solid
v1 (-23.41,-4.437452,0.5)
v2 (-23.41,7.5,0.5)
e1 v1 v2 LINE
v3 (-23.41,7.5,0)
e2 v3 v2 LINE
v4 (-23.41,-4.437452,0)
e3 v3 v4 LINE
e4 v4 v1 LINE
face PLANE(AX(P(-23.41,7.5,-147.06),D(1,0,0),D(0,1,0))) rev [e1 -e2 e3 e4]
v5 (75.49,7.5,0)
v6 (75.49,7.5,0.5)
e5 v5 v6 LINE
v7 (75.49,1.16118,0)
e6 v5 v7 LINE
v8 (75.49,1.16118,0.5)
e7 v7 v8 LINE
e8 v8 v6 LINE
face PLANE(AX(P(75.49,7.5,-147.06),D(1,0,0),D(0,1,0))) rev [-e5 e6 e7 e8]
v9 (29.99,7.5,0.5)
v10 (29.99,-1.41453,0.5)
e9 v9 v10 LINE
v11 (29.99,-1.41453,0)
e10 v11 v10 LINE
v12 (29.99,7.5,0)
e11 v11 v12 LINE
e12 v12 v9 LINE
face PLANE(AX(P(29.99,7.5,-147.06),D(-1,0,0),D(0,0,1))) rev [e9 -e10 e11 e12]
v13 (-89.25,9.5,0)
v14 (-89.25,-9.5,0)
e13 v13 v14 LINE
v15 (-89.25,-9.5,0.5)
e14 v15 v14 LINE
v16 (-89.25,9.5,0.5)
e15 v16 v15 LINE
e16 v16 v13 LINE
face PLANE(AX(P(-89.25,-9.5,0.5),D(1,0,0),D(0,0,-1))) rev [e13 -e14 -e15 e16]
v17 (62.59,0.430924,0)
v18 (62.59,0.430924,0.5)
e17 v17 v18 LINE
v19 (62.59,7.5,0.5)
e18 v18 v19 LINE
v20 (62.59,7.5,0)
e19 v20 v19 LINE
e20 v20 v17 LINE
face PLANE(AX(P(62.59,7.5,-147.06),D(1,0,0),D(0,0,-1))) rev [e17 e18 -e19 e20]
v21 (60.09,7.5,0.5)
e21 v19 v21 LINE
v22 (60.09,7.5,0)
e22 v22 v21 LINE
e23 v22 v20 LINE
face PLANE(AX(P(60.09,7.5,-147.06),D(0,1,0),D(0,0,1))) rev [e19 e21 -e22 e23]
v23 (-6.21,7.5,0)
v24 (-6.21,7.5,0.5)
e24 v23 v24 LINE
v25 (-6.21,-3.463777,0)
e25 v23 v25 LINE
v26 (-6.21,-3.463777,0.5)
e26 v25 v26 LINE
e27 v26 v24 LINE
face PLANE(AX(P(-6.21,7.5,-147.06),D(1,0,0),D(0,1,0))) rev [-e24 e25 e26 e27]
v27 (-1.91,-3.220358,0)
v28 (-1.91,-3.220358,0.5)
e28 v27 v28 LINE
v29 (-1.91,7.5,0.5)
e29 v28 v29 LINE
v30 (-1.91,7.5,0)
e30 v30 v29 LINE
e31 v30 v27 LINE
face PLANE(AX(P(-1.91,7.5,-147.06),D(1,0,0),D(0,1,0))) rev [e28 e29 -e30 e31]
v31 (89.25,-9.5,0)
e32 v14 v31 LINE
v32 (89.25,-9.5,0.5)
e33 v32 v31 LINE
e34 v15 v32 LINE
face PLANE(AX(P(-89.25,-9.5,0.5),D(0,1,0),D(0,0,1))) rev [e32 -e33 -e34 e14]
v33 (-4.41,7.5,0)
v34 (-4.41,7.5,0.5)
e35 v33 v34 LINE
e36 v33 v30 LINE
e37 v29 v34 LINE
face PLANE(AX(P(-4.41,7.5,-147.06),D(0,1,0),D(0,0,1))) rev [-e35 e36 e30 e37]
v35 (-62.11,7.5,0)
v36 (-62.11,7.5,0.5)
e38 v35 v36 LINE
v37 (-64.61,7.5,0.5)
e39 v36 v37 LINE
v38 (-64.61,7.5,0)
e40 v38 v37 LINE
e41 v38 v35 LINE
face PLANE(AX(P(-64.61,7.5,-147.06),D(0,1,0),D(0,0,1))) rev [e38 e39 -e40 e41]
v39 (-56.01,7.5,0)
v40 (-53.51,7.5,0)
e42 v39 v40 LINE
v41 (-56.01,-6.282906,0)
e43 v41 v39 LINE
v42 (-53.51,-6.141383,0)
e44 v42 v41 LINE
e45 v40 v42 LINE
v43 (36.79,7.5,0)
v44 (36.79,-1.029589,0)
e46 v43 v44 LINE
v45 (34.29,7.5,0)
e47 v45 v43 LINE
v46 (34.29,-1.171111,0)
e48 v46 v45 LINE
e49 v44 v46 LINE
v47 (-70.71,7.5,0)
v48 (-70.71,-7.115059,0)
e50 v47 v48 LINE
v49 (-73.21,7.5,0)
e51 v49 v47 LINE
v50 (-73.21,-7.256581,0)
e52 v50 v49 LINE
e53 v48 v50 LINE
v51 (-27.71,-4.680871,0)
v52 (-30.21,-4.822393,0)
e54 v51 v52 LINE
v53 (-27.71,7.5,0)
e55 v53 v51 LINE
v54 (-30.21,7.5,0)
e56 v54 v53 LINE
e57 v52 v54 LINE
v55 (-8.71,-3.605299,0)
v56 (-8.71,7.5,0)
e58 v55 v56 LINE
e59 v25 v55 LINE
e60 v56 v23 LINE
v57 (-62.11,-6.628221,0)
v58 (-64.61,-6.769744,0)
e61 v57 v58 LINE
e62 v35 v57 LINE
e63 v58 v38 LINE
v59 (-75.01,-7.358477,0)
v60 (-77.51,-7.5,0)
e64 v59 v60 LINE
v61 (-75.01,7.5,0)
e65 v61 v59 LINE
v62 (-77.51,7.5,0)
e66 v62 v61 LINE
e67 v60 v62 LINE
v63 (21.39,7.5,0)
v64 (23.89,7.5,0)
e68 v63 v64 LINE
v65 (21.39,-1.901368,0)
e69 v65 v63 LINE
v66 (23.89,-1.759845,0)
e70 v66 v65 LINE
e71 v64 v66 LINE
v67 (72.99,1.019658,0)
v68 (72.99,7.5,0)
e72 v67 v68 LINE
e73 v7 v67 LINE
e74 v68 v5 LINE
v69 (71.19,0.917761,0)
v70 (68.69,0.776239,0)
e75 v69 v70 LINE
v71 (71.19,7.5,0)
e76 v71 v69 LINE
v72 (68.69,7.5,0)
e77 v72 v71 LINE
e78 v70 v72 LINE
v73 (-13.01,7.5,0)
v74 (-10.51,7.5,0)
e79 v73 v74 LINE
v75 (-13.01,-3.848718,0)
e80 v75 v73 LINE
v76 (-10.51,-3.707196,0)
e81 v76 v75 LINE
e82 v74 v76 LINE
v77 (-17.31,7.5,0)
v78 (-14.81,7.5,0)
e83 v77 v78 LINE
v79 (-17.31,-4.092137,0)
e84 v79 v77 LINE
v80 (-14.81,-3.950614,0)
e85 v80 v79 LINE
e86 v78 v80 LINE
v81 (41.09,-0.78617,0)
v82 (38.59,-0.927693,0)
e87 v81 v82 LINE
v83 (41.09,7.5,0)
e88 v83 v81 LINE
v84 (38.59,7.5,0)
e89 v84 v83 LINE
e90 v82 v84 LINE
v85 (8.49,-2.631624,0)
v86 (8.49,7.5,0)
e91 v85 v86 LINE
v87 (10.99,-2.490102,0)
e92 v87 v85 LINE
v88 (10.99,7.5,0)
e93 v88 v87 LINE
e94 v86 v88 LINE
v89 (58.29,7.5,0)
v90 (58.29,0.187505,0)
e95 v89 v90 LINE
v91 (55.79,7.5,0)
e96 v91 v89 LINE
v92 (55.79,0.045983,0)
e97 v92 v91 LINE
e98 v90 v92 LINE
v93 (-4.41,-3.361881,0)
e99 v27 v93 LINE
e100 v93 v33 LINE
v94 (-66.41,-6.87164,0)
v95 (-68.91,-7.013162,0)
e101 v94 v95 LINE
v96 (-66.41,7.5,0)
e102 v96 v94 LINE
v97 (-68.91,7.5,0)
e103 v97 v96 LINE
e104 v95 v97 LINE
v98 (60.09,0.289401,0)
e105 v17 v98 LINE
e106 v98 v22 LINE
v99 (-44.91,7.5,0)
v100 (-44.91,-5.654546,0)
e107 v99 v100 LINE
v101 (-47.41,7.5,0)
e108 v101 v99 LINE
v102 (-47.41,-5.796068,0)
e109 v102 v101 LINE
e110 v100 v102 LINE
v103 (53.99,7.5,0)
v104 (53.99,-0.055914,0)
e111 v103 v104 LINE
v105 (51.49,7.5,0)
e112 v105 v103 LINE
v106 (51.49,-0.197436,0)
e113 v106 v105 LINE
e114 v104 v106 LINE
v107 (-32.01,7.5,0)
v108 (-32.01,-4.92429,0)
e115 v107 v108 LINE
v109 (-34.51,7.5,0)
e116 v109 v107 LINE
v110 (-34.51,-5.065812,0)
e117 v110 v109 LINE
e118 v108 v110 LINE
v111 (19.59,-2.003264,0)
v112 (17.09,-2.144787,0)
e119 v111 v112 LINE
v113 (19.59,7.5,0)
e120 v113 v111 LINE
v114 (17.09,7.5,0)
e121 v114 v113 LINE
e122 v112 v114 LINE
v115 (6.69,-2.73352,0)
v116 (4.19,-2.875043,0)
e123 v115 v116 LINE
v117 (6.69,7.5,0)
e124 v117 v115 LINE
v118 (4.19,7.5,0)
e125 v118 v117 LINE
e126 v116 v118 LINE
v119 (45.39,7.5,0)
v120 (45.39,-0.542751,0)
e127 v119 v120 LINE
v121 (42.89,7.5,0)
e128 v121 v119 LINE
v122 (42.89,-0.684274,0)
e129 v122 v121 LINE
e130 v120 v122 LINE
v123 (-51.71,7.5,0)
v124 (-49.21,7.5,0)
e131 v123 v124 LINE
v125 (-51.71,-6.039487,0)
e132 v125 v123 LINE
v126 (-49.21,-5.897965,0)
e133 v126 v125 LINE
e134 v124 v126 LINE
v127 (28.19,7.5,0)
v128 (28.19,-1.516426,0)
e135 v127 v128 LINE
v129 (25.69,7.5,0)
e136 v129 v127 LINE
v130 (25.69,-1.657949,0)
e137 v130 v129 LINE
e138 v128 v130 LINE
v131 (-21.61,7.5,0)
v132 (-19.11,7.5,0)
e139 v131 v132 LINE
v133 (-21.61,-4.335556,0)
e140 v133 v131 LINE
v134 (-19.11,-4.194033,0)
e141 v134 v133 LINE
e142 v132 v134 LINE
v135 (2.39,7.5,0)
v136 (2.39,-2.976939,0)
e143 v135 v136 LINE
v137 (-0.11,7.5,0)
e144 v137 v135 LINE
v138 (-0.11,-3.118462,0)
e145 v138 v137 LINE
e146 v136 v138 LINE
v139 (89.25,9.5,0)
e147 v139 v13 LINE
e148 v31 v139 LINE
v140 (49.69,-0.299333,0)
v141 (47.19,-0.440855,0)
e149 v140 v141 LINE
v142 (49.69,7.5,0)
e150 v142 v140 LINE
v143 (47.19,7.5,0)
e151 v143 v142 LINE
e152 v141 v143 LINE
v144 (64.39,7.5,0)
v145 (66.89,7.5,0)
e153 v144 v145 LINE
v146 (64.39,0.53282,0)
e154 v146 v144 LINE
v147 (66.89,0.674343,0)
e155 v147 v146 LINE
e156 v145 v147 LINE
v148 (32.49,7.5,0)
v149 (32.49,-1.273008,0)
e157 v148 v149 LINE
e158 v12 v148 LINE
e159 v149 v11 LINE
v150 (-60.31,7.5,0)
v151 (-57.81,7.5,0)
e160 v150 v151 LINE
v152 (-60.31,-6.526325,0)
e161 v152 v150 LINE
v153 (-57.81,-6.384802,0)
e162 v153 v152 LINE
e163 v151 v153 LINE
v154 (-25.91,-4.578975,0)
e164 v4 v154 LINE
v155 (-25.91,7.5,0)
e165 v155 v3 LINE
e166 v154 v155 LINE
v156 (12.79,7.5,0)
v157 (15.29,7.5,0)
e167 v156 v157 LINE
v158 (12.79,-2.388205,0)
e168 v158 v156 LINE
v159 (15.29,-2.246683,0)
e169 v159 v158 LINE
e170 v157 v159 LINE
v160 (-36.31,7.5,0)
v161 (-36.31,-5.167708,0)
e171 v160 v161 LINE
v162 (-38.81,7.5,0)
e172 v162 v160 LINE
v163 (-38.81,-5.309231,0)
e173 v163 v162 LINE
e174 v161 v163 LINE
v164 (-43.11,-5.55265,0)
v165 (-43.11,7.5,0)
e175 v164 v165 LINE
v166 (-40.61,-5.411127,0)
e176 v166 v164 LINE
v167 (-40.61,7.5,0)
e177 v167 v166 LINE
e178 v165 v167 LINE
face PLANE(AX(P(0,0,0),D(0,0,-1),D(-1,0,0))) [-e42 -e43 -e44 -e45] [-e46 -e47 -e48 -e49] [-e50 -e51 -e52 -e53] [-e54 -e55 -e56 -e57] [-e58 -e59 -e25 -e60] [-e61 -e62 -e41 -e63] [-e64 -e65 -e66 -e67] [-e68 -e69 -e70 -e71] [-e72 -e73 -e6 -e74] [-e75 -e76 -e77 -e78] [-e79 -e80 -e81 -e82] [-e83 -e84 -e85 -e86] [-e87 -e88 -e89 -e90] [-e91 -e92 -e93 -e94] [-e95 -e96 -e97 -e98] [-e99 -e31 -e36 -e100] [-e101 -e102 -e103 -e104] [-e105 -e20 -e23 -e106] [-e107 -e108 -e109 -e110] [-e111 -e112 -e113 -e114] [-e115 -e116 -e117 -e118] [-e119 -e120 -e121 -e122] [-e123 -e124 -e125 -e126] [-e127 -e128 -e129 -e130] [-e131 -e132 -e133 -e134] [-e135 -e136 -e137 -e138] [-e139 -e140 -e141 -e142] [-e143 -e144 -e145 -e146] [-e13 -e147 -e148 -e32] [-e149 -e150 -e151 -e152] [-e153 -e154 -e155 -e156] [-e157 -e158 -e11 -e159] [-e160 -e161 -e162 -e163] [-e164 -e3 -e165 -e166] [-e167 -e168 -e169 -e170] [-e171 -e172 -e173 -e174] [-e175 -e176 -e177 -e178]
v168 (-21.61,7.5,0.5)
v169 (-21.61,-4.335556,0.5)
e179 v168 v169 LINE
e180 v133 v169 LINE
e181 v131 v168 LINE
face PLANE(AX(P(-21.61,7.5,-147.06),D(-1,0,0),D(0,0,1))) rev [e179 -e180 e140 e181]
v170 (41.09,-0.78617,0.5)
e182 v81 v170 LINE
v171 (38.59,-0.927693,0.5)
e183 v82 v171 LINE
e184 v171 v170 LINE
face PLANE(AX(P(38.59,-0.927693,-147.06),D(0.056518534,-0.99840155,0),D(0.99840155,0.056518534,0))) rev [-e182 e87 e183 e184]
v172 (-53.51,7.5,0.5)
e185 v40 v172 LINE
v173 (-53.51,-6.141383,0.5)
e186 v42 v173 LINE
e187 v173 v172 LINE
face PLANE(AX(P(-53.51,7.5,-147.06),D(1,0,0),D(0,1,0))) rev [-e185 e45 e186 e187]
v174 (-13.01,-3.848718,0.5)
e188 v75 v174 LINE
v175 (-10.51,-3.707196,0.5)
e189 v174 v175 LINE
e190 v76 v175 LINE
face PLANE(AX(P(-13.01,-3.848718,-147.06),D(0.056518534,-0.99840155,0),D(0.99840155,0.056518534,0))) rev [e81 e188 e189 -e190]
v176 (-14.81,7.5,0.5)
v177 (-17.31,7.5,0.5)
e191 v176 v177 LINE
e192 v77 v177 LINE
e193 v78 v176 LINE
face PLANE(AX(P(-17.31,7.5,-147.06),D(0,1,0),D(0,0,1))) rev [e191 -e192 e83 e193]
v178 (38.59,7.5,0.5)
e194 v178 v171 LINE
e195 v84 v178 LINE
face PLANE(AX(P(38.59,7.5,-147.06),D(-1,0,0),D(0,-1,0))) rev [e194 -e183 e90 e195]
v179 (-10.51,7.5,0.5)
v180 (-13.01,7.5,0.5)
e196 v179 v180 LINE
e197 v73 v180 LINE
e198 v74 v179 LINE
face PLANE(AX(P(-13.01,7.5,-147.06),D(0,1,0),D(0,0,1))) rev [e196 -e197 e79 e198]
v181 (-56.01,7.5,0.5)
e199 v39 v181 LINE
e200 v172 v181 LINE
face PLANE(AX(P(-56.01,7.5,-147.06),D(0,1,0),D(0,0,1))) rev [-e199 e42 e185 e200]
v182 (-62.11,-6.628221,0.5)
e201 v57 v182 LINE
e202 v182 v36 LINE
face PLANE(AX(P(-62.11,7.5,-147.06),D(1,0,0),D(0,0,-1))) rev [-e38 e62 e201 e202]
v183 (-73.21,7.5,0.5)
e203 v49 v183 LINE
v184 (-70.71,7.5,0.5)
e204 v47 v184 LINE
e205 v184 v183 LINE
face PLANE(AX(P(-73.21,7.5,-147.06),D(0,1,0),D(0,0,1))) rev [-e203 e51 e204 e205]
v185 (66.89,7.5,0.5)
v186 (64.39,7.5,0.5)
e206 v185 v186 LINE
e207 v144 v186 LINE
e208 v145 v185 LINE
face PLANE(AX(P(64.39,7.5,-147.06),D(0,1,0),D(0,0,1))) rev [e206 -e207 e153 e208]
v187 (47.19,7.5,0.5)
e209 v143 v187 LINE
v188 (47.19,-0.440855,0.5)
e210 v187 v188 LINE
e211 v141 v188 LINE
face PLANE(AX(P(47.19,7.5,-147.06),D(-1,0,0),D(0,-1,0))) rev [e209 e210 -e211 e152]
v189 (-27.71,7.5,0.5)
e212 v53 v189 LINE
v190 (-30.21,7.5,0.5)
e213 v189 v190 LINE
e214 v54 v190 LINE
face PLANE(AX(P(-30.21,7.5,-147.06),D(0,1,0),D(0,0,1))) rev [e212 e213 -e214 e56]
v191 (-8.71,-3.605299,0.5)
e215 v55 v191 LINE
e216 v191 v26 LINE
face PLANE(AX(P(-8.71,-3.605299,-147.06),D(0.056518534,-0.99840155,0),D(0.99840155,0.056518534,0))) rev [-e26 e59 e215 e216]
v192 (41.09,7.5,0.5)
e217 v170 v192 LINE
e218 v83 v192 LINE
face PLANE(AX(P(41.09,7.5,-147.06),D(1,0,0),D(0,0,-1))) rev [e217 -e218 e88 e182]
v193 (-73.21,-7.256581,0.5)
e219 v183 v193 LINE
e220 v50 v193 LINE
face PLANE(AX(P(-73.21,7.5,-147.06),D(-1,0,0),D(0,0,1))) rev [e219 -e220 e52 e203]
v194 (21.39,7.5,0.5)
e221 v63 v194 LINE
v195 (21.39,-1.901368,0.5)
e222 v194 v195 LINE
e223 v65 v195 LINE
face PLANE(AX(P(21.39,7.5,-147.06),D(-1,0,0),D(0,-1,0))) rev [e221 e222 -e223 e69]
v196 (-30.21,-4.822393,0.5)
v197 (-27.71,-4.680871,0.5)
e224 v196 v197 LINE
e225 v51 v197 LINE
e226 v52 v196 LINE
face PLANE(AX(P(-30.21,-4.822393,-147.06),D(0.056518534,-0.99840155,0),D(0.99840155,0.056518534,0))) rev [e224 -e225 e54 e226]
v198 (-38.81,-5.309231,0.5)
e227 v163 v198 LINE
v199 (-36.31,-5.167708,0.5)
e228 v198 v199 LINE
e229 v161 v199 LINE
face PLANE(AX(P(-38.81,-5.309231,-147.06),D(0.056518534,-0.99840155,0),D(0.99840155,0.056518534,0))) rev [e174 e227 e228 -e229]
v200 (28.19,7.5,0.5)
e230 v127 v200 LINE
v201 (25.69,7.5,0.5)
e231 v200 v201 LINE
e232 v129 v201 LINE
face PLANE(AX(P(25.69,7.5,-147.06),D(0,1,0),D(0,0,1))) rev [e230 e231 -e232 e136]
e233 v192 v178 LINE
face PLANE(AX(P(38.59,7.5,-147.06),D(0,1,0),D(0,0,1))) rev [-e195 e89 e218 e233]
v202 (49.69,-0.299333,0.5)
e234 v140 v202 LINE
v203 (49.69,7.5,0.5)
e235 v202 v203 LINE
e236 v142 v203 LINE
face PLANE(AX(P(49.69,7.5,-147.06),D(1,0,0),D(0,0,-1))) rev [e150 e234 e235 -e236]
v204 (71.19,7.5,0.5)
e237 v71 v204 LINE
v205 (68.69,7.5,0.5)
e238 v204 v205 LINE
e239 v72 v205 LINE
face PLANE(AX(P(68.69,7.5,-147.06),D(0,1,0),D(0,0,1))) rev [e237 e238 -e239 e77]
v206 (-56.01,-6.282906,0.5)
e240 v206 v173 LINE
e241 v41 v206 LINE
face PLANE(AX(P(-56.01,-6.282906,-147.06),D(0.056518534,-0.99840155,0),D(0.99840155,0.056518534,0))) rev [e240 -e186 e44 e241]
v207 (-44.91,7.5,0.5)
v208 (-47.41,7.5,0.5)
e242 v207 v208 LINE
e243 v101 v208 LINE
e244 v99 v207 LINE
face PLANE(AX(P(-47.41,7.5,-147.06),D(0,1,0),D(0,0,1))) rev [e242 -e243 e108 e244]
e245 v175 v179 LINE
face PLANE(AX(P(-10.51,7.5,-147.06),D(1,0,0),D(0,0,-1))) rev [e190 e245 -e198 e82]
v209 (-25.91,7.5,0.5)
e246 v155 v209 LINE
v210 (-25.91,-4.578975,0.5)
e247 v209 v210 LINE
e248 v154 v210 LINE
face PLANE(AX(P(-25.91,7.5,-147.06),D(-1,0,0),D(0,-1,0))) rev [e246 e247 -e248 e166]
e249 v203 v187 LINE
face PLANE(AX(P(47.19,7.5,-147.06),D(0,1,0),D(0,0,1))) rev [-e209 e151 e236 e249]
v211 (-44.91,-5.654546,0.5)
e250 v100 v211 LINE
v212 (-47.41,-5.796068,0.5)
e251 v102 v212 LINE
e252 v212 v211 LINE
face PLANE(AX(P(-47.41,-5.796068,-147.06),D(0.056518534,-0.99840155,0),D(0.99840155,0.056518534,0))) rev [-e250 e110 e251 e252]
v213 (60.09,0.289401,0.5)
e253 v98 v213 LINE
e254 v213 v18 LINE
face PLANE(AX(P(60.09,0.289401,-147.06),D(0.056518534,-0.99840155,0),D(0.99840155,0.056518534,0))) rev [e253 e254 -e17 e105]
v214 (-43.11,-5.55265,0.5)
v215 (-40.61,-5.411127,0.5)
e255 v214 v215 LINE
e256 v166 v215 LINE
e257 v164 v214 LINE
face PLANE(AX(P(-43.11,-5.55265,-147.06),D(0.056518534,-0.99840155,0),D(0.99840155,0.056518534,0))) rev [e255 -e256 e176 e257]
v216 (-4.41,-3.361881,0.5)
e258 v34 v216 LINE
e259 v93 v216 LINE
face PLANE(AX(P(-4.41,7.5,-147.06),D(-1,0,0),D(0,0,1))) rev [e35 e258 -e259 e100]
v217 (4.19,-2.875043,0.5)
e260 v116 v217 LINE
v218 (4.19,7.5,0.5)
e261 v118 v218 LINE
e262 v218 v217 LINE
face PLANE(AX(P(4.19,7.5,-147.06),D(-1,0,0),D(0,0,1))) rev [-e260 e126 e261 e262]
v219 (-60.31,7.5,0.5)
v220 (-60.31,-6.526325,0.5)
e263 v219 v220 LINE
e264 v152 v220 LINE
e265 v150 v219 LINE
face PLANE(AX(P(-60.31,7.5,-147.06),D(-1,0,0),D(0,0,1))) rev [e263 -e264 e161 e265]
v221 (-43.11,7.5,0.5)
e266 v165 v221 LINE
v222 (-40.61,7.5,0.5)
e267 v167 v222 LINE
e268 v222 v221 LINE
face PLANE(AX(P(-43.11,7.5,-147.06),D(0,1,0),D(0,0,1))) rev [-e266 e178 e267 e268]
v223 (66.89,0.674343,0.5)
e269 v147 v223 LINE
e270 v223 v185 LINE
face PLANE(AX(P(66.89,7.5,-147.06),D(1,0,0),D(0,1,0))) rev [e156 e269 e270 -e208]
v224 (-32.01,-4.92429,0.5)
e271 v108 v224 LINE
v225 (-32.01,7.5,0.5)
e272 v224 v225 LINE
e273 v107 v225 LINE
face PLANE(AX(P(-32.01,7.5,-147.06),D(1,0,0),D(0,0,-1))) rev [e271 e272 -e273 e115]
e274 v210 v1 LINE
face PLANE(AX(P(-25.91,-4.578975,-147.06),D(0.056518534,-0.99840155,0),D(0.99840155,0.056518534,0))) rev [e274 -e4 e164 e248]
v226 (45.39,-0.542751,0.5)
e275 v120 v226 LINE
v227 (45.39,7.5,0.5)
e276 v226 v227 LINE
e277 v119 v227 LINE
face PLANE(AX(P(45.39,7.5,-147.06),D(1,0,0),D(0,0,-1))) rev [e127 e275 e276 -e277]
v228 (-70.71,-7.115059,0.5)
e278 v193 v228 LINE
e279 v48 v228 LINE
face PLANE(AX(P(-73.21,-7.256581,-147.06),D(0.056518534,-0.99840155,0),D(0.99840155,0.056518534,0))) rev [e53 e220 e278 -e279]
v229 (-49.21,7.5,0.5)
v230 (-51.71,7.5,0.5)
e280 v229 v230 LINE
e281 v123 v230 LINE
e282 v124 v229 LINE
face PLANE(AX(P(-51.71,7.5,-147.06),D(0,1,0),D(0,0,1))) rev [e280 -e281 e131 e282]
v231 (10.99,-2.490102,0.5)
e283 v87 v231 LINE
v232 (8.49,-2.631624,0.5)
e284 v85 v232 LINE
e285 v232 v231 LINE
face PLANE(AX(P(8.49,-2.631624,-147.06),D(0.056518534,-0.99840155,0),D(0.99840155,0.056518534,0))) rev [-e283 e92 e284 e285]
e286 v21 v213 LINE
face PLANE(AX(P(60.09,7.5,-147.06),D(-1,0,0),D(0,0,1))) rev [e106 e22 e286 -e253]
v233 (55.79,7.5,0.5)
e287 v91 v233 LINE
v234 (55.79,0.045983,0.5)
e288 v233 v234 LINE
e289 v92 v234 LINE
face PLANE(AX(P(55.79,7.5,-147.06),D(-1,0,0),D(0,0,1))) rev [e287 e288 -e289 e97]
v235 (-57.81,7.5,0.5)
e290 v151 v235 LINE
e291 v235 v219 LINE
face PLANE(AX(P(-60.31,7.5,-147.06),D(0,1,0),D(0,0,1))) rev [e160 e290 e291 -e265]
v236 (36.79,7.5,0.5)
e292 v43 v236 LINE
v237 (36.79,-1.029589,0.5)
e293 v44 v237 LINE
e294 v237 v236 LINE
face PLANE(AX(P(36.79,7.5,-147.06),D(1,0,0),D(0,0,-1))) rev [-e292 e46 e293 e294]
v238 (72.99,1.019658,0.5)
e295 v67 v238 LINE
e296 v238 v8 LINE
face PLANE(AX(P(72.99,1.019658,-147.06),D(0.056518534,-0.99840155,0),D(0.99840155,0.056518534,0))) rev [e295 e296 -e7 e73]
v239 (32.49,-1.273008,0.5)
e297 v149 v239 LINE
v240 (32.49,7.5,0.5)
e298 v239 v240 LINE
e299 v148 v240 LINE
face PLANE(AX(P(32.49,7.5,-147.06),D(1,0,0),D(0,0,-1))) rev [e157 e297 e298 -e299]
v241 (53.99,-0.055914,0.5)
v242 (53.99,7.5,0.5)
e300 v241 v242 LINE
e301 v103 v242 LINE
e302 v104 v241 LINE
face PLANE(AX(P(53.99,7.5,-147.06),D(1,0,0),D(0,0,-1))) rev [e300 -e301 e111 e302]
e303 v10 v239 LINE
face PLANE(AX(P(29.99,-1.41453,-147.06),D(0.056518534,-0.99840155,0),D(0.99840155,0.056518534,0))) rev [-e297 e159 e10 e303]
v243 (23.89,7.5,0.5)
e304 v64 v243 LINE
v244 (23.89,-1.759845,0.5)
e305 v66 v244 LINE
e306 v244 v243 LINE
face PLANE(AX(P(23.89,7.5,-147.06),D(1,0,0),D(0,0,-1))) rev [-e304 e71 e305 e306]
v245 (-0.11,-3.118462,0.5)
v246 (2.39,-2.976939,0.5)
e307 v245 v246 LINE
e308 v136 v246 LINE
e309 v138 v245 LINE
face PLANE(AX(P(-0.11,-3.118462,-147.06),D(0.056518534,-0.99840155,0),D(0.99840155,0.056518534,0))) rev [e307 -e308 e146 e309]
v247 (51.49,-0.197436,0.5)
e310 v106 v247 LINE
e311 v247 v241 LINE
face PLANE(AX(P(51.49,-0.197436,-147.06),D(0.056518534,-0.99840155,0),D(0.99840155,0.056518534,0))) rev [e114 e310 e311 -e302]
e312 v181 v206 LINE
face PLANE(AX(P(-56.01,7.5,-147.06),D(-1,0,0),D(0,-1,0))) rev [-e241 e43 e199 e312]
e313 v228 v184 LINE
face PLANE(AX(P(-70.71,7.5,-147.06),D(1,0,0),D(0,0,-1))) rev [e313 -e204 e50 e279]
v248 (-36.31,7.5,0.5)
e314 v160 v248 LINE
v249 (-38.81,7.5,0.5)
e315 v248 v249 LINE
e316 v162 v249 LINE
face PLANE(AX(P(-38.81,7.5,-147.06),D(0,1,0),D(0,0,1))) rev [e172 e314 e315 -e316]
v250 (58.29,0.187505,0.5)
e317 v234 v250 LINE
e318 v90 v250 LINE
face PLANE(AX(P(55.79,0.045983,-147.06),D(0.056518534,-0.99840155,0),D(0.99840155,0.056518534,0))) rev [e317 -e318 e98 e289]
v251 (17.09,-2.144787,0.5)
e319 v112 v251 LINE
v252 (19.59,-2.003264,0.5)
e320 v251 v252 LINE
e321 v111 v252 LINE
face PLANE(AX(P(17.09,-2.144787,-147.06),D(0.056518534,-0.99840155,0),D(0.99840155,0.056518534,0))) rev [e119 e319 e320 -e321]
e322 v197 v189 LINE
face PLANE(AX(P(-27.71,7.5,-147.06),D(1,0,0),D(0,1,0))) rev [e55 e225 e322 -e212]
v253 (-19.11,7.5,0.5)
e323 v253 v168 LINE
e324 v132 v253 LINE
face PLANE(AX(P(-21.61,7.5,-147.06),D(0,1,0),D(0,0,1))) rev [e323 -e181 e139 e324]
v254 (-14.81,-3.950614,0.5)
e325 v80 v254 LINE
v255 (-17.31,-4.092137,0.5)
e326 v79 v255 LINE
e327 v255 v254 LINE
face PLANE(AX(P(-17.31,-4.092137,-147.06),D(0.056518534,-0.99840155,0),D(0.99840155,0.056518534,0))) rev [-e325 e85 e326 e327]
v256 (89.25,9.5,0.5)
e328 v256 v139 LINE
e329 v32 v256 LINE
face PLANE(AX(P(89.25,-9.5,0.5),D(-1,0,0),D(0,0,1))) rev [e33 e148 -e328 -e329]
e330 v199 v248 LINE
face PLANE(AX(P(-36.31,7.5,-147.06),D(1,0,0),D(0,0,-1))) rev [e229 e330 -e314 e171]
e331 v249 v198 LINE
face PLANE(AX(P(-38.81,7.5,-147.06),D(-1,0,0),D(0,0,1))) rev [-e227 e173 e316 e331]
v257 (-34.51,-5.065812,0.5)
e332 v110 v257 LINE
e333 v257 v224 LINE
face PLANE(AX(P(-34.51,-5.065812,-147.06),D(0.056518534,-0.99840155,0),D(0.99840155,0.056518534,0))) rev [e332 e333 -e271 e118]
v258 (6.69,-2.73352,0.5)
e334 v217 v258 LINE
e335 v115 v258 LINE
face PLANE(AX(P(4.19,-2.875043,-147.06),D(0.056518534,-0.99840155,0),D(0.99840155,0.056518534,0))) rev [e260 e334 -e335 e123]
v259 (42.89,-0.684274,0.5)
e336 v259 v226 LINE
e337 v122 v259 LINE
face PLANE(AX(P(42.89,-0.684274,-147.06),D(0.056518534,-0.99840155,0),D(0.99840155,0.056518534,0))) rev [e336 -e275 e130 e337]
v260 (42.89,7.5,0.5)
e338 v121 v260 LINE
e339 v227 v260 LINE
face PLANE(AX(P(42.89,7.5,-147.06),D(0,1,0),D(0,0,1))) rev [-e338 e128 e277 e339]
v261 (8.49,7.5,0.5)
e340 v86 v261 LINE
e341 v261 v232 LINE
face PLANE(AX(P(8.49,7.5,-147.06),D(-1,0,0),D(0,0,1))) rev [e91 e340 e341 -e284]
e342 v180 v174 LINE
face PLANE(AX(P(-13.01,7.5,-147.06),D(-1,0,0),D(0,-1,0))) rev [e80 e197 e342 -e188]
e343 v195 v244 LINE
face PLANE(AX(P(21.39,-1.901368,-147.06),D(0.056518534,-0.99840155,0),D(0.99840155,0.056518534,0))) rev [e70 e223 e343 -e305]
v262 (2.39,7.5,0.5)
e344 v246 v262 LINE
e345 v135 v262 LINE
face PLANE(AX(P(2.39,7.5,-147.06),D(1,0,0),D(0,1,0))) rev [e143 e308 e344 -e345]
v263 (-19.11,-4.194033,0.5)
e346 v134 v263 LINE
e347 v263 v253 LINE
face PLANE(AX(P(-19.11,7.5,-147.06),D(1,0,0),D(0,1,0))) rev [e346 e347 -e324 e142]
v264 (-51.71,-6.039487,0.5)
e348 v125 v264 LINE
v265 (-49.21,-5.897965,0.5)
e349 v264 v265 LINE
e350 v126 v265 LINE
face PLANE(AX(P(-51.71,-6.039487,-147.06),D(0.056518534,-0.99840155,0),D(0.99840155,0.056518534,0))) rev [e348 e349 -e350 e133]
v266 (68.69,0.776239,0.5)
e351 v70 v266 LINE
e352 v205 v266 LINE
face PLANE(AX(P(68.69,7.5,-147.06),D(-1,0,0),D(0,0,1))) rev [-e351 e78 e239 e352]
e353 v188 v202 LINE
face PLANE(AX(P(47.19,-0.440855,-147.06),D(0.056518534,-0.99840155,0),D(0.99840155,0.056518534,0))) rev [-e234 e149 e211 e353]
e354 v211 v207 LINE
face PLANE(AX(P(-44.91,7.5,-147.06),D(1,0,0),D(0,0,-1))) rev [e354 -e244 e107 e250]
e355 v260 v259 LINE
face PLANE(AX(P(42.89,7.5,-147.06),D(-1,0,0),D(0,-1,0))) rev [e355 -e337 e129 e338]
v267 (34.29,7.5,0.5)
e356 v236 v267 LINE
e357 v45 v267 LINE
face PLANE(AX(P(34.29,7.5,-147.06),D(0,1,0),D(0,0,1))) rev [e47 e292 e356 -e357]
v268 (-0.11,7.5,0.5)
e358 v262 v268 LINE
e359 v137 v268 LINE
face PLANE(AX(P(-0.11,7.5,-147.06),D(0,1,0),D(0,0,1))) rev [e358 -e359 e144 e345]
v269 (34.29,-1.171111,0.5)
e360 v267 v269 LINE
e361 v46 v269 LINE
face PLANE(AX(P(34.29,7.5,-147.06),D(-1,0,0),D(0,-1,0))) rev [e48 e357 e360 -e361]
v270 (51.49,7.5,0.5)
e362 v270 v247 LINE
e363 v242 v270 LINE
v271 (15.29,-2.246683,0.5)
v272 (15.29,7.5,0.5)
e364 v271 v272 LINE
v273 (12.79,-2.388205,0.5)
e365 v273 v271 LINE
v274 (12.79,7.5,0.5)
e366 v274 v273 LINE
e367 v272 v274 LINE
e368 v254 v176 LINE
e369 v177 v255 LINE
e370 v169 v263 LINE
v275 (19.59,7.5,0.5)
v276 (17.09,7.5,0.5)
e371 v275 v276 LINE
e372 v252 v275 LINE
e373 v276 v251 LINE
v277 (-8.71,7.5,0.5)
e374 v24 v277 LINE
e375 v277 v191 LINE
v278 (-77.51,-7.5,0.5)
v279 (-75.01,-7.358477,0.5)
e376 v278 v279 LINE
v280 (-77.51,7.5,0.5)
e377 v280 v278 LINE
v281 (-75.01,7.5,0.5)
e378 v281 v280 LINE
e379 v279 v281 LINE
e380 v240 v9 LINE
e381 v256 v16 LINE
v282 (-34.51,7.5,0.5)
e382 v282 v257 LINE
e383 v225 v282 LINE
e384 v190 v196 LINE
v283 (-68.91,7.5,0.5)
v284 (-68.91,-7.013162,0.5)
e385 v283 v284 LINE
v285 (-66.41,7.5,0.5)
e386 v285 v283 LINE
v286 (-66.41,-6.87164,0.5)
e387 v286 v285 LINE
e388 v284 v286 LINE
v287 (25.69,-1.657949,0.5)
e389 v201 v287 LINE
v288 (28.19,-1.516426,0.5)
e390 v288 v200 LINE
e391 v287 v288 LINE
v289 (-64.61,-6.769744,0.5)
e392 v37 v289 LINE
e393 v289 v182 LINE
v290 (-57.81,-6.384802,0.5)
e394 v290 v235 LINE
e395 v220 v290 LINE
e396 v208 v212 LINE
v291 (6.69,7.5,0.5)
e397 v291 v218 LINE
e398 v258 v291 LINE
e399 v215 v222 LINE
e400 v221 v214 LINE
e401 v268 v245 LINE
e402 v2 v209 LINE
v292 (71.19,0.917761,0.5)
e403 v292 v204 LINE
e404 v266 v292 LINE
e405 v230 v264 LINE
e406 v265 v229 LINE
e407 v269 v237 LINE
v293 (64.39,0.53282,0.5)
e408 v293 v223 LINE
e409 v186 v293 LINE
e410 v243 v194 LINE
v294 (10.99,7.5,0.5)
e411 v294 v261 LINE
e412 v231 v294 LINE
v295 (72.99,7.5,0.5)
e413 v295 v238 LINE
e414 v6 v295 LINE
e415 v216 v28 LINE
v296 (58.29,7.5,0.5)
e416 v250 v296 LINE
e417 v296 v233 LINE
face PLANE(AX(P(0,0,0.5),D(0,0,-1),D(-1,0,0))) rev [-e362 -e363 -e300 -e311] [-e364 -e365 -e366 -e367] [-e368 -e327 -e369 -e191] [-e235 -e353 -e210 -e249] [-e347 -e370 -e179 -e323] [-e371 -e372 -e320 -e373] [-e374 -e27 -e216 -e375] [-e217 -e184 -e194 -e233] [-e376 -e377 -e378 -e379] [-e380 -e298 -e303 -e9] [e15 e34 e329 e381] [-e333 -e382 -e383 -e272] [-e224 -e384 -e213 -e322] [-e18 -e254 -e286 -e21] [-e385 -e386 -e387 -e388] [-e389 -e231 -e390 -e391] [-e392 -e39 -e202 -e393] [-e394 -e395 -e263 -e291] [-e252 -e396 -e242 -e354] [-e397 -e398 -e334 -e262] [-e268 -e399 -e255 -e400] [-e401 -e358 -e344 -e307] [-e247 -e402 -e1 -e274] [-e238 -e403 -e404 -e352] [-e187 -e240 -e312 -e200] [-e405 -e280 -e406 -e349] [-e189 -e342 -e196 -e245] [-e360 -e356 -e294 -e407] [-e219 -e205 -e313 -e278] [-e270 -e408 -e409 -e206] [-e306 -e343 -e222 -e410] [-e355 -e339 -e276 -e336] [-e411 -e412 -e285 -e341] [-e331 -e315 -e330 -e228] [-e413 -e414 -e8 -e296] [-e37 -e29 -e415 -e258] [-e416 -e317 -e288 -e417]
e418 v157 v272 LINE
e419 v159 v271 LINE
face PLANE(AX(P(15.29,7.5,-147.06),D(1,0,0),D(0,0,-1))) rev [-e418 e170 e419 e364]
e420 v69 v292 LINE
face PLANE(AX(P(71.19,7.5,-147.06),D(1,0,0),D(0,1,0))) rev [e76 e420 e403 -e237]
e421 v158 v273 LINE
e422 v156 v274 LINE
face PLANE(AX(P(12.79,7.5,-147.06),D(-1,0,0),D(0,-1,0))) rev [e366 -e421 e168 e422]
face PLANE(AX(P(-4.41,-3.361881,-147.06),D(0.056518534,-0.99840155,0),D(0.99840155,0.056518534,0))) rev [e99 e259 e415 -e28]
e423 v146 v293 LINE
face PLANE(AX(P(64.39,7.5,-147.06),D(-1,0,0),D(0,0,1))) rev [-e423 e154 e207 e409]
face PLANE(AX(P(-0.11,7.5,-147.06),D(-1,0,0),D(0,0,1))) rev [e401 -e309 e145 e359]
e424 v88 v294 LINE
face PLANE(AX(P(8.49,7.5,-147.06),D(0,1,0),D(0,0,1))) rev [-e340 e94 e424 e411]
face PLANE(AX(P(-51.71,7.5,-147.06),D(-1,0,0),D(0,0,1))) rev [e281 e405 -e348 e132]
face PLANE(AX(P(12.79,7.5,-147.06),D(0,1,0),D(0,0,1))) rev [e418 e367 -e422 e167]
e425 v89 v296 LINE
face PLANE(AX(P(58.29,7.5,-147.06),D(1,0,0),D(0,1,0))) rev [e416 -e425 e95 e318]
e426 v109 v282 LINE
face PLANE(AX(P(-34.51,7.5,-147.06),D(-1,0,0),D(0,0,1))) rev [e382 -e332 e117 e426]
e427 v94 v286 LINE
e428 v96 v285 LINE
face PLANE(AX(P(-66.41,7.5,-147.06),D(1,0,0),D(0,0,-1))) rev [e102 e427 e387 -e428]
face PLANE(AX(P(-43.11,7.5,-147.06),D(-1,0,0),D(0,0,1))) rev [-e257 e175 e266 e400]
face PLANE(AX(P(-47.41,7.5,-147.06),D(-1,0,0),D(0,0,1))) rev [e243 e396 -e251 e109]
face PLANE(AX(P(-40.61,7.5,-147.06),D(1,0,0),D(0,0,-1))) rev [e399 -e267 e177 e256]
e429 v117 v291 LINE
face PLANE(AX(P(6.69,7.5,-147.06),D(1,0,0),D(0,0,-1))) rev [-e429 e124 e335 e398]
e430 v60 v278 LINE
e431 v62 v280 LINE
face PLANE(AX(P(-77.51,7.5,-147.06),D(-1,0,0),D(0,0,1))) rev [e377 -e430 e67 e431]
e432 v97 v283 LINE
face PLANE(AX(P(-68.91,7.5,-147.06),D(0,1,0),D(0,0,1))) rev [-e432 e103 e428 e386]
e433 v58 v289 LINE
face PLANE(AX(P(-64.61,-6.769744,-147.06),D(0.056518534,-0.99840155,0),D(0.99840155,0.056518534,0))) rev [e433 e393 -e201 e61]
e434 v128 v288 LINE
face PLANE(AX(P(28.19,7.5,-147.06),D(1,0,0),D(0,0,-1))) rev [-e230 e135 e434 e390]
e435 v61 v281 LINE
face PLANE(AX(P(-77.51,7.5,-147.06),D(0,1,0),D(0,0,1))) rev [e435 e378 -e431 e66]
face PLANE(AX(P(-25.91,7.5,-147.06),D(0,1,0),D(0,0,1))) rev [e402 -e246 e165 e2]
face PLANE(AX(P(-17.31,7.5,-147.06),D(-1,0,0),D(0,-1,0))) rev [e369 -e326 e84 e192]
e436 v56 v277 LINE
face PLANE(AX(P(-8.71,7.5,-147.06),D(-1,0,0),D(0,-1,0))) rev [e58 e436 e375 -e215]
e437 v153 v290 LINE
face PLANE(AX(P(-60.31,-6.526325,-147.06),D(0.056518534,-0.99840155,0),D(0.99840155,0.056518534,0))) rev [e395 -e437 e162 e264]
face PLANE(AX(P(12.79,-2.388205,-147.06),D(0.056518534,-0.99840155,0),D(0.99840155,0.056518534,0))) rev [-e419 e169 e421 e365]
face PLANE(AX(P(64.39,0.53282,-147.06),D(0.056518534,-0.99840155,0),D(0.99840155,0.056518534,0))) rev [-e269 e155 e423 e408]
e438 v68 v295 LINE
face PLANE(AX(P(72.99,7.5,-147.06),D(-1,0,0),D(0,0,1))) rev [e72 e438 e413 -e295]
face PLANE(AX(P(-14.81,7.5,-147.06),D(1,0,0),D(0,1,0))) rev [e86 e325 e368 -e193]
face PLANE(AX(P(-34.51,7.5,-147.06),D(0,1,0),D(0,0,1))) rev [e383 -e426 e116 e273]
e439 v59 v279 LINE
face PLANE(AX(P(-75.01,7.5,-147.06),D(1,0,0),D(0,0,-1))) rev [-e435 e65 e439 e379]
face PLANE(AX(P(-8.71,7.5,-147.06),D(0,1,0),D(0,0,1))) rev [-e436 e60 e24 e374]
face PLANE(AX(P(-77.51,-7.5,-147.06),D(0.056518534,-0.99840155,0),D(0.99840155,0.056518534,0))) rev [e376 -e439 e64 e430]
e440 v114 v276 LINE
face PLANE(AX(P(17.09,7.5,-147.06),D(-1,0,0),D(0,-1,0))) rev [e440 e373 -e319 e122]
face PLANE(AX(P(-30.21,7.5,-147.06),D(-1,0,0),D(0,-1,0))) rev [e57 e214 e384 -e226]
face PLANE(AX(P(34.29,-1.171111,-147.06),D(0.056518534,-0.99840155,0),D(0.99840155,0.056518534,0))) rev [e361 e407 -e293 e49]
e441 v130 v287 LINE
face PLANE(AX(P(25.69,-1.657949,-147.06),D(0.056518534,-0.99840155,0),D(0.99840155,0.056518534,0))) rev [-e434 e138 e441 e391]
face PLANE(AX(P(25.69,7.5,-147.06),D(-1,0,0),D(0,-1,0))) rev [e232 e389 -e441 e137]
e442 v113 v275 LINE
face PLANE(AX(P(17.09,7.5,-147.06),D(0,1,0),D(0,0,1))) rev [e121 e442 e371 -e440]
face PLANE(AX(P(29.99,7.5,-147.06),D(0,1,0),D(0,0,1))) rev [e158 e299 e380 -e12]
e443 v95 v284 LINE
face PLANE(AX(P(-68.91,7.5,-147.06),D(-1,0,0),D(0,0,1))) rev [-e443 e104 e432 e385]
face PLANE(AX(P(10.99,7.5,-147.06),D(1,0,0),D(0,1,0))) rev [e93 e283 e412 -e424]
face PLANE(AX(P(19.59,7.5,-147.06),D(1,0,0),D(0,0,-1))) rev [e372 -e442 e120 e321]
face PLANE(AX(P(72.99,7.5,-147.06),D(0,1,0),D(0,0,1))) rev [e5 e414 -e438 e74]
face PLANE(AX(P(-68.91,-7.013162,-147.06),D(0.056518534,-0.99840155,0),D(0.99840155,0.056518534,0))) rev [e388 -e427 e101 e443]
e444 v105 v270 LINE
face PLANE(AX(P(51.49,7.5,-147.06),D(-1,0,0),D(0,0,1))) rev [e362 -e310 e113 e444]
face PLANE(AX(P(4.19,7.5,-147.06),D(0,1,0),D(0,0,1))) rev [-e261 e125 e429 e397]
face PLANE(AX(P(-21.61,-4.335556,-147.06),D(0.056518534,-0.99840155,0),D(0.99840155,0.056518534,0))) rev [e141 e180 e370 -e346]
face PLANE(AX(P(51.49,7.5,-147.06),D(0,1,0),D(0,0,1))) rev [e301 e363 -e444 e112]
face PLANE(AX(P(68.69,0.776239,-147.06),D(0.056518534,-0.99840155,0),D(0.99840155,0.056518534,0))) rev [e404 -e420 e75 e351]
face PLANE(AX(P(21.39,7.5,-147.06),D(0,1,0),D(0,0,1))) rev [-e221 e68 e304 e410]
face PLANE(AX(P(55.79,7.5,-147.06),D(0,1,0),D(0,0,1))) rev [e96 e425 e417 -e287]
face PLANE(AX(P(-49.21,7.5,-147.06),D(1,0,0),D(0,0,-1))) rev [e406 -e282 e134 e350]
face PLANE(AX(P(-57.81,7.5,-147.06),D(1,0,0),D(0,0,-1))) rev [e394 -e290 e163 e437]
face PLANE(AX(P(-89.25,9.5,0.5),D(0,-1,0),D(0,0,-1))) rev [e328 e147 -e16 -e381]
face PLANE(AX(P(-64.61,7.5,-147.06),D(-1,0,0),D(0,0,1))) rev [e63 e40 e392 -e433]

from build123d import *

# Parameters (mm, degrees)
SKETCH1_W           = 178.5
SKETCH1_H           = 19
BOSS_EXTRUDE1_DEPTH = 0.5
CUT_EXTRUDE1_DEPTH  = 147.56


with BuildPart() as part:
    # Sketch1 → Boss-Extrude1 (new body)
    with BuildSketch(Plane.XY):
        Rectangle(SKETCH1_W, SKETCH1_H)
    extrude(amount=BOSS_EXTRUDE1_DEPTH)

    # Sketch2 → Cut-Extrude1 (cut)
    with BuildSketch(Plane.XY.offset(0.5)):
        Polygon((-77.51, 7.5), (-75.01, 7.5), (-75.01, -7.358477447), (-77.51, -7.5), align=None)
        Polygon((-70.71, 7.5), (-70.71, -7.115058656), (-73.21, -7.256581209), (-73.21, 7.5), align=None)
        Polygon((-66.41, 7.5), (-66.41, -6.871639865), (-68.91, -7.013162418), (-68.91, 7.5), align=None)
        Polygon((-62.11, 7.5), (-62.11, -6.628221074), (-64.61, -6.769743627), (-64.61, 7.5), align=None)
        Polygon((-57.81, 7.5), (-57.81, -6.384802283), (-60.31, -6.526324836), (-60.31, 7.5), align=None)
        Polygon((-53.51, 7.5), (-53.51, -6.141383492), (-56.01, -6.282906045), (-56.01, 7.5), align=None)
        Polygon((-49.21, 7.5), (-49.21, -5.897964701), (-51.71, -6.039487254), (-51.71, 7.5), align=None)
        Polygon((-44.91, 7.5), (-44.91, -5.65454591), (-47.41, -5.796068463), (-47.41, 7.5), align=None)
        Polygon((-40.61, 7.5), (-40.61, -5.411127119), (-43.11, -5.552649672), (-43.11, 7.5), align=None)
        Polygon((-36.31, 7.5), (-36.31, -5.167708328), (-38.81, -5.309230881), (-38.81, 7.5), align=None)
        Polygon((-32.01, 7.5), (-32.01, -4.924289537), (-34.51, -5.06581209), (-34.51, 7.5), align=None)
        Polygon((-27.71, 7.5), (-27.71, -4.680870746), (-30.21, -4.822393299), (-30.21, 7.5), align=None)
        Polygon((-23.41, 7.5), (-23.41, -4.437451955), (-25.91, -4.578974508), (-25.91, 7.5), align=None)
        Polygon((-19.11, 7.5), (-19.11, -4.194033164), (-21.61, -4.335555717), (-21.61, 7.5), align=None)
        Polygon((-14.81, 7.5), (-14.81, -3.950614373), (-17.31, -4.092136926), (-17.31, 7.5), align=None)
        Polygon((-10.51, 7.5), (-10.51, -3.707195582), (-13.01, -3.848718135), (-13.01, 7.5), align=None)
        Polygon((-6.21, 7.5), (-6.21, -3.463776791), (-8.71, -3.605299344), (-8.71, 7.5), align=None)
        Polygon((-1.91, 7.5), (-1.91, -3.220358), (-4.41, -3.361880553), (-4.41, 7.5), align=None)
        Polygon((2.39, 7.5), (2.39, -2.976939209), (-0.11, -3.118461762), (-0.11, 7.5), align=None)
        Polygon((6.69, 7.5), (6.69, -2.733520418), (4.19, -2.875042971), (4.19, 7.5), align=None)
        Polygon((10.99, 7.5), (10.99, -2.490101627), (8.49, -2.63162418), (8.49, 7.5), align=None)
        Polygon((15.29, 7.5), (15.29, -2.246682836), (12.79, -2.388205389), (12.79, 7.5), align=None)
        Polygon((19.59, 7.5), (19.59, -2.003264045), (17.09, -2.144786598), (17.09, 7.5), align=None)
        Polygon((23.89, 7.5), (23.89, -1.759845254), (21.39, -1.901367807), (21.39, 7.5), align=None)
        Polygon((28.19, 7.5), (28.19, -1.516426463), (25.69, -1.657949016), (25.69, 7.5), align=None)
        Polygon((32.49, 7.5), (32.49, -1.273007672), (29.99, -1.414530225), (29.99, 7.5), align=None)
        Polygon((36.79, 7.5), (36.79, -1.029588881), (34.29, -1.171111434), (34.29, 7.5), align=None)
        Polygon((41.09, 7.5), (41.09, -0.78617009), (38.59, -0.927692643), (38.59, 7.5), align=None)
        Polygon((45.39, 7.5), (45.39, -0.542751299), (42.89, -0.684273852), (42.89, 7.5), align=None)
        Polygon((49.69, 7.5), (49.69, -0.299332508), (47.19, -0.440855061), (47.19, 7.5), align=None)
        Polygon((53.99, 7.5), (53.99, -0.055913717), (51.49, -0.19743627), (51.49, 7.5), align=None)
        Polygon((58.29, 7.5), (58.29, 0.187505074), (55.79, 0.045982521), (55.79, 7.5), align=None)
        Polygon((62.59, 7.5), (62.59, 0.430923865), (60.09, 0.289401312), (60.09, 7.5), align=None)
        Polygon((66.89, 7.5), (66.89, 0.674342656), (64.39, 0.532820103), (64.39, 7.5), align=None)
        Polygon((71.19, 7.5), (71.19, 0.917761447), (68.69, 0.776238894), (68.69, 7.5), align=None)
        Polygon((75.49, 7.5), (75.49, 1.161180238), (72.99, 1.019657685), (72.99, 7.5), align=None)
    extrude(amount=-CUT_EXTRUDE1_DEPTH, mode=Mode.SUBTRACT)


solid = part.part
